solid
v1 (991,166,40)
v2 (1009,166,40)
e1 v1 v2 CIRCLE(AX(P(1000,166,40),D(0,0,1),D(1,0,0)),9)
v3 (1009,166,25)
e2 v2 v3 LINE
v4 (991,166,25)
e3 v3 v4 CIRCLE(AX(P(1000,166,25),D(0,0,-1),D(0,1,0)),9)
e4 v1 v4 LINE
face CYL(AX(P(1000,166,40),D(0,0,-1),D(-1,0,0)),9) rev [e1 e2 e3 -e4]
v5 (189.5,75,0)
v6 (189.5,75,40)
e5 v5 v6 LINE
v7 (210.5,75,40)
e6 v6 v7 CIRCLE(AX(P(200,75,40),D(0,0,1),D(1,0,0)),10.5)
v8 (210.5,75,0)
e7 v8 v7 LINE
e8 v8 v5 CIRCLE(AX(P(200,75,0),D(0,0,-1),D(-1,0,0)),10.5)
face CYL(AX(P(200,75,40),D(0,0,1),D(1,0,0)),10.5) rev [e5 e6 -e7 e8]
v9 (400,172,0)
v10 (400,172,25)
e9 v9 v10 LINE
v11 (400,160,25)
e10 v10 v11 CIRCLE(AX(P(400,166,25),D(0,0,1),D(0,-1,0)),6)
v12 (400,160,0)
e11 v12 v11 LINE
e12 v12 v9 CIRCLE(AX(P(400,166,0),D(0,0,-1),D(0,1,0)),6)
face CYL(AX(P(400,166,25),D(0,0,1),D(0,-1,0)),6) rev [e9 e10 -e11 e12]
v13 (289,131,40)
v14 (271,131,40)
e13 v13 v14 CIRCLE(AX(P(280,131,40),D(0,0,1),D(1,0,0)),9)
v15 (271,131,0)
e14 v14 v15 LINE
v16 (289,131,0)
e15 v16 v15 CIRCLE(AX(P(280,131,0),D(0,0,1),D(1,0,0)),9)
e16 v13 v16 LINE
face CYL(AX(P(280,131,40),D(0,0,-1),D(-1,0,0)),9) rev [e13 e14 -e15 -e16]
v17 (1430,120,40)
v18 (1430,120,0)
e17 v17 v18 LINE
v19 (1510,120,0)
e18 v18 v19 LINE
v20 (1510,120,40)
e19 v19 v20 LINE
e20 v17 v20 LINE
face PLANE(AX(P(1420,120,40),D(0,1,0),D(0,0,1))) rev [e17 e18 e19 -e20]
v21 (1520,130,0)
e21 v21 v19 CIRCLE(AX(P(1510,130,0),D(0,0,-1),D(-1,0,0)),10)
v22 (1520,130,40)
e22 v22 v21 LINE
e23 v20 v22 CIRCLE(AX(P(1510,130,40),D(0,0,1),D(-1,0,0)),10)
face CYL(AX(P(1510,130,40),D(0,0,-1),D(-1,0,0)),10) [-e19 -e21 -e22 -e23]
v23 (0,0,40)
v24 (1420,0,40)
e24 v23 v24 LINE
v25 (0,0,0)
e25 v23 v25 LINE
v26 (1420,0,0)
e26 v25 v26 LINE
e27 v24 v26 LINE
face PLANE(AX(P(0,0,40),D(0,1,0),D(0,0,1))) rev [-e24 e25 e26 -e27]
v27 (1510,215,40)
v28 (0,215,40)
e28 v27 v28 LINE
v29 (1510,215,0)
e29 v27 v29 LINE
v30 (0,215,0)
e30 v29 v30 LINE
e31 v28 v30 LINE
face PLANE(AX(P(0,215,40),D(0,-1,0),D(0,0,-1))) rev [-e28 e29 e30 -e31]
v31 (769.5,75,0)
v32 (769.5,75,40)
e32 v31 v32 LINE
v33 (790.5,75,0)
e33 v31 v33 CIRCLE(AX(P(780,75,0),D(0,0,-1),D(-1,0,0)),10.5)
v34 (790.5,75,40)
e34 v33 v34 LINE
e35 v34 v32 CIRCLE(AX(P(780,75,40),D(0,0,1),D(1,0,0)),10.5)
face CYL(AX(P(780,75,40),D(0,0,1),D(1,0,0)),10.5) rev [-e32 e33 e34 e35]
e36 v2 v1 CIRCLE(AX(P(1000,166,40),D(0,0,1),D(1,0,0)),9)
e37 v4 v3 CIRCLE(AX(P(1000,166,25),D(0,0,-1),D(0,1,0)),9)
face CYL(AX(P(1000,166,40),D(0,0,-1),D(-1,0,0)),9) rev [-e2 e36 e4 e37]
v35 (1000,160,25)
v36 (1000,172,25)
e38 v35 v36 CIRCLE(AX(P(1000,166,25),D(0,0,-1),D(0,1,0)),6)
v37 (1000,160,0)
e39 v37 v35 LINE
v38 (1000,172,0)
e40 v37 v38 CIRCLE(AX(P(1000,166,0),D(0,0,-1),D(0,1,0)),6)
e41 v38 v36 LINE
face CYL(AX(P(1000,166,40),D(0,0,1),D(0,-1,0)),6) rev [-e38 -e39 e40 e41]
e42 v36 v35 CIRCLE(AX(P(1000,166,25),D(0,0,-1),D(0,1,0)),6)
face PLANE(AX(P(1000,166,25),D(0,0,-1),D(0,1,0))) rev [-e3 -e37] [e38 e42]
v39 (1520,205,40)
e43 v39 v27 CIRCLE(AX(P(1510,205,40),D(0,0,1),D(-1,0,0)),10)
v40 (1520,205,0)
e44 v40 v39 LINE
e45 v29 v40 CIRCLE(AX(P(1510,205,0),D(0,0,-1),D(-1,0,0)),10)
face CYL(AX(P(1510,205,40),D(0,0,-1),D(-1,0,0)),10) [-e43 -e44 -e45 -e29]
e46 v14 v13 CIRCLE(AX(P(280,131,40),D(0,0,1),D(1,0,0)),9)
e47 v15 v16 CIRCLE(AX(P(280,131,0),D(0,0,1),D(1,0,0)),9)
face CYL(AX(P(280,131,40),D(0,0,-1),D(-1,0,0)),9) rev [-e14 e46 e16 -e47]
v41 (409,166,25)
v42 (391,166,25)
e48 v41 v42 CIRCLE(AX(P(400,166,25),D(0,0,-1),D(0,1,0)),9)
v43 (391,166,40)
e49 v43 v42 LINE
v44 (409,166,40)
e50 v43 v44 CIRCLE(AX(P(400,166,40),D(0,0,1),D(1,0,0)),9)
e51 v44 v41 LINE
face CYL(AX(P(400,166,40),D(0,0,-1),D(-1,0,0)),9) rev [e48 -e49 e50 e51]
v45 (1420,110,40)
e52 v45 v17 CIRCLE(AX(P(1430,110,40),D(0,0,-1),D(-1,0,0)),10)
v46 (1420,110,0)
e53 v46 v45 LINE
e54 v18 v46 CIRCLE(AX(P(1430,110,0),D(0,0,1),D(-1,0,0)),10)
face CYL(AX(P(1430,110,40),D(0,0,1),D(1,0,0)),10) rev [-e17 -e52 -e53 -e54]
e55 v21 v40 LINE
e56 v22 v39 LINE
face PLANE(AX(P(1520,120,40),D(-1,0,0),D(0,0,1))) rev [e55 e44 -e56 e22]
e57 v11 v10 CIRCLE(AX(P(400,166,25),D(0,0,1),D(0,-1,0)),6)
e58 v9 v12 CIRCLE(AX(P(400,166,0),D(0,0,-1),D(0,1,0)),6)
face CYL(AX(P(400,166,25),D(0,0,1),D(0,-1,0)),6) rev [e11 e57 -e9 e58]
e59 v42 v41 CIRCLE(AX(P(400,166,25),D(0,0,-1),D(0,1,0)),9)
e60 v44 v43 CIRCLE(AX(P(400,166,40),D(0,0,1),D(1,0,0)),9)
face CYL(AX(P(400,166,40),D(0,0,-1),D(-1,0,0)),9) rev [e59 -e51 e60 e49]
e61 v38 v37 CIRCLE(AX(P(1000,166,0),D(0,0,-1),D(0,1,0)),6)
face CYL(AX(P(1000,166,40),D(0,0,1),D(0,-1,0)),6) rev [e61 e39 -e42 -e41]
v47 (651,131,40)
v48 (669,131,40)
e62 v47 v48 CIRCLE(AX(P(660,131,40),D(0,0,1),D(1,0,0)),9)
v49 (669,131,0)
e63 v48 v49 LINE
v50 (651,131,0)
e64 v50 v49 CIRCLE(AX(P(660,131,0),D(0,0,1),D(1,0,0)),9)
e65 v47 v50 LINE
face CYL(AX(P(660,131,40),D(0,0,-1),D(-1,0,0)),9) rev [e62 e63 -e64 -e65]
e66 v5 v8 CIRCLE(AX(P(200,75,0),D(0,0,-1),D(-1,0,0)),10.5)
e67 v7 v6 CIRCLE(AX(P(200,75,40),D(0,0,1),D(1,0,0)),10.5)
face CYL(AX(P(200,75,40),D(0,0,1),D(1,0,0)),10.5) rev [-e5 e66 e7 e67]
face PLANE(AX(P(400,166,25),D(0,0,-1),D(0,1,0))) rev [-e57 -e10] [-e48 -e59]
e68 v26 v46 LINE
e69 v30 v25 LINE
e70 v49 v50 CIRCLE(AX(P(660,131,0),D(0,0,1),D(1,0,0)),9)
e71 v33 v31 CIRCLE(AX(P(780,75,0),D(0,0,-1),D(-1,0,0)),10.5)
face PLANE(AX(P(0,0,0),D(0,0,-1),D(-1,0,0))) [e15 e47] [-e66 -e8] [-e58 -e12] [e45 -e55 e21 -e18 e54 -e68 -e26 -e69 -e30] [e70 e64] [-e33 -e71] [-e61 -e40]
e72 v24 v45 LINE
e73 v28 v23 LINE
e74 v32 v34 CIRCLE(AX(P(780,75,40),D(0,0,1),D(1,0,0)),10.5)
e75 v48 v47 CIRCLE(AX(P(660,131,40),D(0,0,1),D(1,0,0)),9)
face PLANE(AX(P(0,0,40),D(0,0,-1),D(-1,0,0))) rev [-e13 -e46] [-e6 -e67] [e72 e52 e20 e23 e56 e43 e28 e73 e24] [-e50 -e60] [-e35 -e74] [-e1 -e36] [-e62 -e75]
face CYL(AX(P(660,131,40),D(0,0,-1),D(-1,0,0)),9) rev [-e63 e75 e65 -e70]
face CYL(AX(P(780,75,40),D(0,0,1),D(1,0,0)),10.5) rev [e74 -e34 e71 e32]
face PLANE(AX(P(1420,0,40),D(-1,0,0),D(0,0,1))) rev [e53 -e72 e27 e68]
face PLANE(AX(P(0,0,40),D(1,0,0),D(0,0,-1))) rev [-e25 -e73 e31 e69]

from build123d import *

# Parameters (mm, degrees)
SKETCH1_R                        = 9
BOSS_EXTRUDE1_DEPTH              = 40
M24_TAPPED_HOLE1_D               = 21
FILLET1_R                        = 10
SKETCH3_R                        = 9
SKETCH3_R_2                      = 9.680977079
BOSS_EXTRUDE2_DEPTH              = 25
M14_TAPPED_HOLE1_D               = 12
M14_TAPPED_HOLE1_DEPTH           = 40
M14_TAPPED_HOLE1_ON_FACE_2_D     = 12
M14_TAPPED_HOLE1_ON_FACE_2_DEPTH = 40


with BuildPart() as part:
    # Sketch1 → Boss-Extrude1 (new body)
    with BuildSketch(Plane.XY):
        Polygon((0, 215), (1520, 215), (1520, 120), (1420, 120), (1420, 0), (0, 0), align=None)
        with Locations((400, 166)):
            Circle(SKETCH1_R, mode=Mode.SUBTRACT)
        with Locations((280, 131)):
            Circle(SKETCH1_R, mode=Mode.SUBTRACT)
        with Locations((660, 131)):
            Circle(SKETCH1_R, mode=Mode.SUBTRACT)
        with Locations((1000, 166)):
            Circle(SKETCH1_R, mode=Mode.SUBTRACT)
    extrude(amount=BOSS_EXTRUDE1_DEPTH)

    # M24 Tapped Hole1 (through all)
    with Locations(Plane(origin=(780, 75, 40), x_dir=(1, 0, 0), z_dir=(0, 0, 1))):
        with Locations((0, 0), (-580, 0)):
            Hole(M24_TAPPED_HOLE1_D / 2)

    # Fillet1
    fillet1_edges = [part.edges().sort_by_distance(p)[0] for p in [
        (1520, 215, 20),
        (1520, 120, 20),
        (1420, 120, 20),
    ]]
    fillet(fillet1_edges, radius=FILLET1_R)

    # Sketch3 → Boss-Extrude2 (add)
    with BuildSketch(Plane(origin=(0, 0, 0), x_dir=(-1, 0, 0), z_dir=(0, 0, -1))):
        with Locations(Location((-1000, 166, 0), (0, 0, 90))):
            Circle(SKETCH3_R)
        with Locations((-400, 166)):
            Circle(SKETCH3_R_2)
    extrude(amount=-BOSS_EXTRUDE2_DEPTH)

    # M14 Tapped Hole1
    with Locations(Plane(origin=(1000, 166, 40), x_dir=(0, 1, 0), z_dir=(0, 0, 1))):
        with Locations((0, 0)):
            Hole(M14_TAPPED_HOLE1_D / 2, depth=M14_TAPPED_HOLE1_DEPTH)

    # M14 Tapped Hole1 on face 2
    with Locations(Plane(origin=(400, 166, 25), x_dir=(1, 0, 0), z_dir=(0, 0, 1))):
        with Locations((0, 0)):
            Hole(M14_TAPPED_HOLE1_ON_FACE_2_D / 2, depth=M14_TAPPED_HOLE1_ON_FACE_2_DEPTH)


solid = part.part
